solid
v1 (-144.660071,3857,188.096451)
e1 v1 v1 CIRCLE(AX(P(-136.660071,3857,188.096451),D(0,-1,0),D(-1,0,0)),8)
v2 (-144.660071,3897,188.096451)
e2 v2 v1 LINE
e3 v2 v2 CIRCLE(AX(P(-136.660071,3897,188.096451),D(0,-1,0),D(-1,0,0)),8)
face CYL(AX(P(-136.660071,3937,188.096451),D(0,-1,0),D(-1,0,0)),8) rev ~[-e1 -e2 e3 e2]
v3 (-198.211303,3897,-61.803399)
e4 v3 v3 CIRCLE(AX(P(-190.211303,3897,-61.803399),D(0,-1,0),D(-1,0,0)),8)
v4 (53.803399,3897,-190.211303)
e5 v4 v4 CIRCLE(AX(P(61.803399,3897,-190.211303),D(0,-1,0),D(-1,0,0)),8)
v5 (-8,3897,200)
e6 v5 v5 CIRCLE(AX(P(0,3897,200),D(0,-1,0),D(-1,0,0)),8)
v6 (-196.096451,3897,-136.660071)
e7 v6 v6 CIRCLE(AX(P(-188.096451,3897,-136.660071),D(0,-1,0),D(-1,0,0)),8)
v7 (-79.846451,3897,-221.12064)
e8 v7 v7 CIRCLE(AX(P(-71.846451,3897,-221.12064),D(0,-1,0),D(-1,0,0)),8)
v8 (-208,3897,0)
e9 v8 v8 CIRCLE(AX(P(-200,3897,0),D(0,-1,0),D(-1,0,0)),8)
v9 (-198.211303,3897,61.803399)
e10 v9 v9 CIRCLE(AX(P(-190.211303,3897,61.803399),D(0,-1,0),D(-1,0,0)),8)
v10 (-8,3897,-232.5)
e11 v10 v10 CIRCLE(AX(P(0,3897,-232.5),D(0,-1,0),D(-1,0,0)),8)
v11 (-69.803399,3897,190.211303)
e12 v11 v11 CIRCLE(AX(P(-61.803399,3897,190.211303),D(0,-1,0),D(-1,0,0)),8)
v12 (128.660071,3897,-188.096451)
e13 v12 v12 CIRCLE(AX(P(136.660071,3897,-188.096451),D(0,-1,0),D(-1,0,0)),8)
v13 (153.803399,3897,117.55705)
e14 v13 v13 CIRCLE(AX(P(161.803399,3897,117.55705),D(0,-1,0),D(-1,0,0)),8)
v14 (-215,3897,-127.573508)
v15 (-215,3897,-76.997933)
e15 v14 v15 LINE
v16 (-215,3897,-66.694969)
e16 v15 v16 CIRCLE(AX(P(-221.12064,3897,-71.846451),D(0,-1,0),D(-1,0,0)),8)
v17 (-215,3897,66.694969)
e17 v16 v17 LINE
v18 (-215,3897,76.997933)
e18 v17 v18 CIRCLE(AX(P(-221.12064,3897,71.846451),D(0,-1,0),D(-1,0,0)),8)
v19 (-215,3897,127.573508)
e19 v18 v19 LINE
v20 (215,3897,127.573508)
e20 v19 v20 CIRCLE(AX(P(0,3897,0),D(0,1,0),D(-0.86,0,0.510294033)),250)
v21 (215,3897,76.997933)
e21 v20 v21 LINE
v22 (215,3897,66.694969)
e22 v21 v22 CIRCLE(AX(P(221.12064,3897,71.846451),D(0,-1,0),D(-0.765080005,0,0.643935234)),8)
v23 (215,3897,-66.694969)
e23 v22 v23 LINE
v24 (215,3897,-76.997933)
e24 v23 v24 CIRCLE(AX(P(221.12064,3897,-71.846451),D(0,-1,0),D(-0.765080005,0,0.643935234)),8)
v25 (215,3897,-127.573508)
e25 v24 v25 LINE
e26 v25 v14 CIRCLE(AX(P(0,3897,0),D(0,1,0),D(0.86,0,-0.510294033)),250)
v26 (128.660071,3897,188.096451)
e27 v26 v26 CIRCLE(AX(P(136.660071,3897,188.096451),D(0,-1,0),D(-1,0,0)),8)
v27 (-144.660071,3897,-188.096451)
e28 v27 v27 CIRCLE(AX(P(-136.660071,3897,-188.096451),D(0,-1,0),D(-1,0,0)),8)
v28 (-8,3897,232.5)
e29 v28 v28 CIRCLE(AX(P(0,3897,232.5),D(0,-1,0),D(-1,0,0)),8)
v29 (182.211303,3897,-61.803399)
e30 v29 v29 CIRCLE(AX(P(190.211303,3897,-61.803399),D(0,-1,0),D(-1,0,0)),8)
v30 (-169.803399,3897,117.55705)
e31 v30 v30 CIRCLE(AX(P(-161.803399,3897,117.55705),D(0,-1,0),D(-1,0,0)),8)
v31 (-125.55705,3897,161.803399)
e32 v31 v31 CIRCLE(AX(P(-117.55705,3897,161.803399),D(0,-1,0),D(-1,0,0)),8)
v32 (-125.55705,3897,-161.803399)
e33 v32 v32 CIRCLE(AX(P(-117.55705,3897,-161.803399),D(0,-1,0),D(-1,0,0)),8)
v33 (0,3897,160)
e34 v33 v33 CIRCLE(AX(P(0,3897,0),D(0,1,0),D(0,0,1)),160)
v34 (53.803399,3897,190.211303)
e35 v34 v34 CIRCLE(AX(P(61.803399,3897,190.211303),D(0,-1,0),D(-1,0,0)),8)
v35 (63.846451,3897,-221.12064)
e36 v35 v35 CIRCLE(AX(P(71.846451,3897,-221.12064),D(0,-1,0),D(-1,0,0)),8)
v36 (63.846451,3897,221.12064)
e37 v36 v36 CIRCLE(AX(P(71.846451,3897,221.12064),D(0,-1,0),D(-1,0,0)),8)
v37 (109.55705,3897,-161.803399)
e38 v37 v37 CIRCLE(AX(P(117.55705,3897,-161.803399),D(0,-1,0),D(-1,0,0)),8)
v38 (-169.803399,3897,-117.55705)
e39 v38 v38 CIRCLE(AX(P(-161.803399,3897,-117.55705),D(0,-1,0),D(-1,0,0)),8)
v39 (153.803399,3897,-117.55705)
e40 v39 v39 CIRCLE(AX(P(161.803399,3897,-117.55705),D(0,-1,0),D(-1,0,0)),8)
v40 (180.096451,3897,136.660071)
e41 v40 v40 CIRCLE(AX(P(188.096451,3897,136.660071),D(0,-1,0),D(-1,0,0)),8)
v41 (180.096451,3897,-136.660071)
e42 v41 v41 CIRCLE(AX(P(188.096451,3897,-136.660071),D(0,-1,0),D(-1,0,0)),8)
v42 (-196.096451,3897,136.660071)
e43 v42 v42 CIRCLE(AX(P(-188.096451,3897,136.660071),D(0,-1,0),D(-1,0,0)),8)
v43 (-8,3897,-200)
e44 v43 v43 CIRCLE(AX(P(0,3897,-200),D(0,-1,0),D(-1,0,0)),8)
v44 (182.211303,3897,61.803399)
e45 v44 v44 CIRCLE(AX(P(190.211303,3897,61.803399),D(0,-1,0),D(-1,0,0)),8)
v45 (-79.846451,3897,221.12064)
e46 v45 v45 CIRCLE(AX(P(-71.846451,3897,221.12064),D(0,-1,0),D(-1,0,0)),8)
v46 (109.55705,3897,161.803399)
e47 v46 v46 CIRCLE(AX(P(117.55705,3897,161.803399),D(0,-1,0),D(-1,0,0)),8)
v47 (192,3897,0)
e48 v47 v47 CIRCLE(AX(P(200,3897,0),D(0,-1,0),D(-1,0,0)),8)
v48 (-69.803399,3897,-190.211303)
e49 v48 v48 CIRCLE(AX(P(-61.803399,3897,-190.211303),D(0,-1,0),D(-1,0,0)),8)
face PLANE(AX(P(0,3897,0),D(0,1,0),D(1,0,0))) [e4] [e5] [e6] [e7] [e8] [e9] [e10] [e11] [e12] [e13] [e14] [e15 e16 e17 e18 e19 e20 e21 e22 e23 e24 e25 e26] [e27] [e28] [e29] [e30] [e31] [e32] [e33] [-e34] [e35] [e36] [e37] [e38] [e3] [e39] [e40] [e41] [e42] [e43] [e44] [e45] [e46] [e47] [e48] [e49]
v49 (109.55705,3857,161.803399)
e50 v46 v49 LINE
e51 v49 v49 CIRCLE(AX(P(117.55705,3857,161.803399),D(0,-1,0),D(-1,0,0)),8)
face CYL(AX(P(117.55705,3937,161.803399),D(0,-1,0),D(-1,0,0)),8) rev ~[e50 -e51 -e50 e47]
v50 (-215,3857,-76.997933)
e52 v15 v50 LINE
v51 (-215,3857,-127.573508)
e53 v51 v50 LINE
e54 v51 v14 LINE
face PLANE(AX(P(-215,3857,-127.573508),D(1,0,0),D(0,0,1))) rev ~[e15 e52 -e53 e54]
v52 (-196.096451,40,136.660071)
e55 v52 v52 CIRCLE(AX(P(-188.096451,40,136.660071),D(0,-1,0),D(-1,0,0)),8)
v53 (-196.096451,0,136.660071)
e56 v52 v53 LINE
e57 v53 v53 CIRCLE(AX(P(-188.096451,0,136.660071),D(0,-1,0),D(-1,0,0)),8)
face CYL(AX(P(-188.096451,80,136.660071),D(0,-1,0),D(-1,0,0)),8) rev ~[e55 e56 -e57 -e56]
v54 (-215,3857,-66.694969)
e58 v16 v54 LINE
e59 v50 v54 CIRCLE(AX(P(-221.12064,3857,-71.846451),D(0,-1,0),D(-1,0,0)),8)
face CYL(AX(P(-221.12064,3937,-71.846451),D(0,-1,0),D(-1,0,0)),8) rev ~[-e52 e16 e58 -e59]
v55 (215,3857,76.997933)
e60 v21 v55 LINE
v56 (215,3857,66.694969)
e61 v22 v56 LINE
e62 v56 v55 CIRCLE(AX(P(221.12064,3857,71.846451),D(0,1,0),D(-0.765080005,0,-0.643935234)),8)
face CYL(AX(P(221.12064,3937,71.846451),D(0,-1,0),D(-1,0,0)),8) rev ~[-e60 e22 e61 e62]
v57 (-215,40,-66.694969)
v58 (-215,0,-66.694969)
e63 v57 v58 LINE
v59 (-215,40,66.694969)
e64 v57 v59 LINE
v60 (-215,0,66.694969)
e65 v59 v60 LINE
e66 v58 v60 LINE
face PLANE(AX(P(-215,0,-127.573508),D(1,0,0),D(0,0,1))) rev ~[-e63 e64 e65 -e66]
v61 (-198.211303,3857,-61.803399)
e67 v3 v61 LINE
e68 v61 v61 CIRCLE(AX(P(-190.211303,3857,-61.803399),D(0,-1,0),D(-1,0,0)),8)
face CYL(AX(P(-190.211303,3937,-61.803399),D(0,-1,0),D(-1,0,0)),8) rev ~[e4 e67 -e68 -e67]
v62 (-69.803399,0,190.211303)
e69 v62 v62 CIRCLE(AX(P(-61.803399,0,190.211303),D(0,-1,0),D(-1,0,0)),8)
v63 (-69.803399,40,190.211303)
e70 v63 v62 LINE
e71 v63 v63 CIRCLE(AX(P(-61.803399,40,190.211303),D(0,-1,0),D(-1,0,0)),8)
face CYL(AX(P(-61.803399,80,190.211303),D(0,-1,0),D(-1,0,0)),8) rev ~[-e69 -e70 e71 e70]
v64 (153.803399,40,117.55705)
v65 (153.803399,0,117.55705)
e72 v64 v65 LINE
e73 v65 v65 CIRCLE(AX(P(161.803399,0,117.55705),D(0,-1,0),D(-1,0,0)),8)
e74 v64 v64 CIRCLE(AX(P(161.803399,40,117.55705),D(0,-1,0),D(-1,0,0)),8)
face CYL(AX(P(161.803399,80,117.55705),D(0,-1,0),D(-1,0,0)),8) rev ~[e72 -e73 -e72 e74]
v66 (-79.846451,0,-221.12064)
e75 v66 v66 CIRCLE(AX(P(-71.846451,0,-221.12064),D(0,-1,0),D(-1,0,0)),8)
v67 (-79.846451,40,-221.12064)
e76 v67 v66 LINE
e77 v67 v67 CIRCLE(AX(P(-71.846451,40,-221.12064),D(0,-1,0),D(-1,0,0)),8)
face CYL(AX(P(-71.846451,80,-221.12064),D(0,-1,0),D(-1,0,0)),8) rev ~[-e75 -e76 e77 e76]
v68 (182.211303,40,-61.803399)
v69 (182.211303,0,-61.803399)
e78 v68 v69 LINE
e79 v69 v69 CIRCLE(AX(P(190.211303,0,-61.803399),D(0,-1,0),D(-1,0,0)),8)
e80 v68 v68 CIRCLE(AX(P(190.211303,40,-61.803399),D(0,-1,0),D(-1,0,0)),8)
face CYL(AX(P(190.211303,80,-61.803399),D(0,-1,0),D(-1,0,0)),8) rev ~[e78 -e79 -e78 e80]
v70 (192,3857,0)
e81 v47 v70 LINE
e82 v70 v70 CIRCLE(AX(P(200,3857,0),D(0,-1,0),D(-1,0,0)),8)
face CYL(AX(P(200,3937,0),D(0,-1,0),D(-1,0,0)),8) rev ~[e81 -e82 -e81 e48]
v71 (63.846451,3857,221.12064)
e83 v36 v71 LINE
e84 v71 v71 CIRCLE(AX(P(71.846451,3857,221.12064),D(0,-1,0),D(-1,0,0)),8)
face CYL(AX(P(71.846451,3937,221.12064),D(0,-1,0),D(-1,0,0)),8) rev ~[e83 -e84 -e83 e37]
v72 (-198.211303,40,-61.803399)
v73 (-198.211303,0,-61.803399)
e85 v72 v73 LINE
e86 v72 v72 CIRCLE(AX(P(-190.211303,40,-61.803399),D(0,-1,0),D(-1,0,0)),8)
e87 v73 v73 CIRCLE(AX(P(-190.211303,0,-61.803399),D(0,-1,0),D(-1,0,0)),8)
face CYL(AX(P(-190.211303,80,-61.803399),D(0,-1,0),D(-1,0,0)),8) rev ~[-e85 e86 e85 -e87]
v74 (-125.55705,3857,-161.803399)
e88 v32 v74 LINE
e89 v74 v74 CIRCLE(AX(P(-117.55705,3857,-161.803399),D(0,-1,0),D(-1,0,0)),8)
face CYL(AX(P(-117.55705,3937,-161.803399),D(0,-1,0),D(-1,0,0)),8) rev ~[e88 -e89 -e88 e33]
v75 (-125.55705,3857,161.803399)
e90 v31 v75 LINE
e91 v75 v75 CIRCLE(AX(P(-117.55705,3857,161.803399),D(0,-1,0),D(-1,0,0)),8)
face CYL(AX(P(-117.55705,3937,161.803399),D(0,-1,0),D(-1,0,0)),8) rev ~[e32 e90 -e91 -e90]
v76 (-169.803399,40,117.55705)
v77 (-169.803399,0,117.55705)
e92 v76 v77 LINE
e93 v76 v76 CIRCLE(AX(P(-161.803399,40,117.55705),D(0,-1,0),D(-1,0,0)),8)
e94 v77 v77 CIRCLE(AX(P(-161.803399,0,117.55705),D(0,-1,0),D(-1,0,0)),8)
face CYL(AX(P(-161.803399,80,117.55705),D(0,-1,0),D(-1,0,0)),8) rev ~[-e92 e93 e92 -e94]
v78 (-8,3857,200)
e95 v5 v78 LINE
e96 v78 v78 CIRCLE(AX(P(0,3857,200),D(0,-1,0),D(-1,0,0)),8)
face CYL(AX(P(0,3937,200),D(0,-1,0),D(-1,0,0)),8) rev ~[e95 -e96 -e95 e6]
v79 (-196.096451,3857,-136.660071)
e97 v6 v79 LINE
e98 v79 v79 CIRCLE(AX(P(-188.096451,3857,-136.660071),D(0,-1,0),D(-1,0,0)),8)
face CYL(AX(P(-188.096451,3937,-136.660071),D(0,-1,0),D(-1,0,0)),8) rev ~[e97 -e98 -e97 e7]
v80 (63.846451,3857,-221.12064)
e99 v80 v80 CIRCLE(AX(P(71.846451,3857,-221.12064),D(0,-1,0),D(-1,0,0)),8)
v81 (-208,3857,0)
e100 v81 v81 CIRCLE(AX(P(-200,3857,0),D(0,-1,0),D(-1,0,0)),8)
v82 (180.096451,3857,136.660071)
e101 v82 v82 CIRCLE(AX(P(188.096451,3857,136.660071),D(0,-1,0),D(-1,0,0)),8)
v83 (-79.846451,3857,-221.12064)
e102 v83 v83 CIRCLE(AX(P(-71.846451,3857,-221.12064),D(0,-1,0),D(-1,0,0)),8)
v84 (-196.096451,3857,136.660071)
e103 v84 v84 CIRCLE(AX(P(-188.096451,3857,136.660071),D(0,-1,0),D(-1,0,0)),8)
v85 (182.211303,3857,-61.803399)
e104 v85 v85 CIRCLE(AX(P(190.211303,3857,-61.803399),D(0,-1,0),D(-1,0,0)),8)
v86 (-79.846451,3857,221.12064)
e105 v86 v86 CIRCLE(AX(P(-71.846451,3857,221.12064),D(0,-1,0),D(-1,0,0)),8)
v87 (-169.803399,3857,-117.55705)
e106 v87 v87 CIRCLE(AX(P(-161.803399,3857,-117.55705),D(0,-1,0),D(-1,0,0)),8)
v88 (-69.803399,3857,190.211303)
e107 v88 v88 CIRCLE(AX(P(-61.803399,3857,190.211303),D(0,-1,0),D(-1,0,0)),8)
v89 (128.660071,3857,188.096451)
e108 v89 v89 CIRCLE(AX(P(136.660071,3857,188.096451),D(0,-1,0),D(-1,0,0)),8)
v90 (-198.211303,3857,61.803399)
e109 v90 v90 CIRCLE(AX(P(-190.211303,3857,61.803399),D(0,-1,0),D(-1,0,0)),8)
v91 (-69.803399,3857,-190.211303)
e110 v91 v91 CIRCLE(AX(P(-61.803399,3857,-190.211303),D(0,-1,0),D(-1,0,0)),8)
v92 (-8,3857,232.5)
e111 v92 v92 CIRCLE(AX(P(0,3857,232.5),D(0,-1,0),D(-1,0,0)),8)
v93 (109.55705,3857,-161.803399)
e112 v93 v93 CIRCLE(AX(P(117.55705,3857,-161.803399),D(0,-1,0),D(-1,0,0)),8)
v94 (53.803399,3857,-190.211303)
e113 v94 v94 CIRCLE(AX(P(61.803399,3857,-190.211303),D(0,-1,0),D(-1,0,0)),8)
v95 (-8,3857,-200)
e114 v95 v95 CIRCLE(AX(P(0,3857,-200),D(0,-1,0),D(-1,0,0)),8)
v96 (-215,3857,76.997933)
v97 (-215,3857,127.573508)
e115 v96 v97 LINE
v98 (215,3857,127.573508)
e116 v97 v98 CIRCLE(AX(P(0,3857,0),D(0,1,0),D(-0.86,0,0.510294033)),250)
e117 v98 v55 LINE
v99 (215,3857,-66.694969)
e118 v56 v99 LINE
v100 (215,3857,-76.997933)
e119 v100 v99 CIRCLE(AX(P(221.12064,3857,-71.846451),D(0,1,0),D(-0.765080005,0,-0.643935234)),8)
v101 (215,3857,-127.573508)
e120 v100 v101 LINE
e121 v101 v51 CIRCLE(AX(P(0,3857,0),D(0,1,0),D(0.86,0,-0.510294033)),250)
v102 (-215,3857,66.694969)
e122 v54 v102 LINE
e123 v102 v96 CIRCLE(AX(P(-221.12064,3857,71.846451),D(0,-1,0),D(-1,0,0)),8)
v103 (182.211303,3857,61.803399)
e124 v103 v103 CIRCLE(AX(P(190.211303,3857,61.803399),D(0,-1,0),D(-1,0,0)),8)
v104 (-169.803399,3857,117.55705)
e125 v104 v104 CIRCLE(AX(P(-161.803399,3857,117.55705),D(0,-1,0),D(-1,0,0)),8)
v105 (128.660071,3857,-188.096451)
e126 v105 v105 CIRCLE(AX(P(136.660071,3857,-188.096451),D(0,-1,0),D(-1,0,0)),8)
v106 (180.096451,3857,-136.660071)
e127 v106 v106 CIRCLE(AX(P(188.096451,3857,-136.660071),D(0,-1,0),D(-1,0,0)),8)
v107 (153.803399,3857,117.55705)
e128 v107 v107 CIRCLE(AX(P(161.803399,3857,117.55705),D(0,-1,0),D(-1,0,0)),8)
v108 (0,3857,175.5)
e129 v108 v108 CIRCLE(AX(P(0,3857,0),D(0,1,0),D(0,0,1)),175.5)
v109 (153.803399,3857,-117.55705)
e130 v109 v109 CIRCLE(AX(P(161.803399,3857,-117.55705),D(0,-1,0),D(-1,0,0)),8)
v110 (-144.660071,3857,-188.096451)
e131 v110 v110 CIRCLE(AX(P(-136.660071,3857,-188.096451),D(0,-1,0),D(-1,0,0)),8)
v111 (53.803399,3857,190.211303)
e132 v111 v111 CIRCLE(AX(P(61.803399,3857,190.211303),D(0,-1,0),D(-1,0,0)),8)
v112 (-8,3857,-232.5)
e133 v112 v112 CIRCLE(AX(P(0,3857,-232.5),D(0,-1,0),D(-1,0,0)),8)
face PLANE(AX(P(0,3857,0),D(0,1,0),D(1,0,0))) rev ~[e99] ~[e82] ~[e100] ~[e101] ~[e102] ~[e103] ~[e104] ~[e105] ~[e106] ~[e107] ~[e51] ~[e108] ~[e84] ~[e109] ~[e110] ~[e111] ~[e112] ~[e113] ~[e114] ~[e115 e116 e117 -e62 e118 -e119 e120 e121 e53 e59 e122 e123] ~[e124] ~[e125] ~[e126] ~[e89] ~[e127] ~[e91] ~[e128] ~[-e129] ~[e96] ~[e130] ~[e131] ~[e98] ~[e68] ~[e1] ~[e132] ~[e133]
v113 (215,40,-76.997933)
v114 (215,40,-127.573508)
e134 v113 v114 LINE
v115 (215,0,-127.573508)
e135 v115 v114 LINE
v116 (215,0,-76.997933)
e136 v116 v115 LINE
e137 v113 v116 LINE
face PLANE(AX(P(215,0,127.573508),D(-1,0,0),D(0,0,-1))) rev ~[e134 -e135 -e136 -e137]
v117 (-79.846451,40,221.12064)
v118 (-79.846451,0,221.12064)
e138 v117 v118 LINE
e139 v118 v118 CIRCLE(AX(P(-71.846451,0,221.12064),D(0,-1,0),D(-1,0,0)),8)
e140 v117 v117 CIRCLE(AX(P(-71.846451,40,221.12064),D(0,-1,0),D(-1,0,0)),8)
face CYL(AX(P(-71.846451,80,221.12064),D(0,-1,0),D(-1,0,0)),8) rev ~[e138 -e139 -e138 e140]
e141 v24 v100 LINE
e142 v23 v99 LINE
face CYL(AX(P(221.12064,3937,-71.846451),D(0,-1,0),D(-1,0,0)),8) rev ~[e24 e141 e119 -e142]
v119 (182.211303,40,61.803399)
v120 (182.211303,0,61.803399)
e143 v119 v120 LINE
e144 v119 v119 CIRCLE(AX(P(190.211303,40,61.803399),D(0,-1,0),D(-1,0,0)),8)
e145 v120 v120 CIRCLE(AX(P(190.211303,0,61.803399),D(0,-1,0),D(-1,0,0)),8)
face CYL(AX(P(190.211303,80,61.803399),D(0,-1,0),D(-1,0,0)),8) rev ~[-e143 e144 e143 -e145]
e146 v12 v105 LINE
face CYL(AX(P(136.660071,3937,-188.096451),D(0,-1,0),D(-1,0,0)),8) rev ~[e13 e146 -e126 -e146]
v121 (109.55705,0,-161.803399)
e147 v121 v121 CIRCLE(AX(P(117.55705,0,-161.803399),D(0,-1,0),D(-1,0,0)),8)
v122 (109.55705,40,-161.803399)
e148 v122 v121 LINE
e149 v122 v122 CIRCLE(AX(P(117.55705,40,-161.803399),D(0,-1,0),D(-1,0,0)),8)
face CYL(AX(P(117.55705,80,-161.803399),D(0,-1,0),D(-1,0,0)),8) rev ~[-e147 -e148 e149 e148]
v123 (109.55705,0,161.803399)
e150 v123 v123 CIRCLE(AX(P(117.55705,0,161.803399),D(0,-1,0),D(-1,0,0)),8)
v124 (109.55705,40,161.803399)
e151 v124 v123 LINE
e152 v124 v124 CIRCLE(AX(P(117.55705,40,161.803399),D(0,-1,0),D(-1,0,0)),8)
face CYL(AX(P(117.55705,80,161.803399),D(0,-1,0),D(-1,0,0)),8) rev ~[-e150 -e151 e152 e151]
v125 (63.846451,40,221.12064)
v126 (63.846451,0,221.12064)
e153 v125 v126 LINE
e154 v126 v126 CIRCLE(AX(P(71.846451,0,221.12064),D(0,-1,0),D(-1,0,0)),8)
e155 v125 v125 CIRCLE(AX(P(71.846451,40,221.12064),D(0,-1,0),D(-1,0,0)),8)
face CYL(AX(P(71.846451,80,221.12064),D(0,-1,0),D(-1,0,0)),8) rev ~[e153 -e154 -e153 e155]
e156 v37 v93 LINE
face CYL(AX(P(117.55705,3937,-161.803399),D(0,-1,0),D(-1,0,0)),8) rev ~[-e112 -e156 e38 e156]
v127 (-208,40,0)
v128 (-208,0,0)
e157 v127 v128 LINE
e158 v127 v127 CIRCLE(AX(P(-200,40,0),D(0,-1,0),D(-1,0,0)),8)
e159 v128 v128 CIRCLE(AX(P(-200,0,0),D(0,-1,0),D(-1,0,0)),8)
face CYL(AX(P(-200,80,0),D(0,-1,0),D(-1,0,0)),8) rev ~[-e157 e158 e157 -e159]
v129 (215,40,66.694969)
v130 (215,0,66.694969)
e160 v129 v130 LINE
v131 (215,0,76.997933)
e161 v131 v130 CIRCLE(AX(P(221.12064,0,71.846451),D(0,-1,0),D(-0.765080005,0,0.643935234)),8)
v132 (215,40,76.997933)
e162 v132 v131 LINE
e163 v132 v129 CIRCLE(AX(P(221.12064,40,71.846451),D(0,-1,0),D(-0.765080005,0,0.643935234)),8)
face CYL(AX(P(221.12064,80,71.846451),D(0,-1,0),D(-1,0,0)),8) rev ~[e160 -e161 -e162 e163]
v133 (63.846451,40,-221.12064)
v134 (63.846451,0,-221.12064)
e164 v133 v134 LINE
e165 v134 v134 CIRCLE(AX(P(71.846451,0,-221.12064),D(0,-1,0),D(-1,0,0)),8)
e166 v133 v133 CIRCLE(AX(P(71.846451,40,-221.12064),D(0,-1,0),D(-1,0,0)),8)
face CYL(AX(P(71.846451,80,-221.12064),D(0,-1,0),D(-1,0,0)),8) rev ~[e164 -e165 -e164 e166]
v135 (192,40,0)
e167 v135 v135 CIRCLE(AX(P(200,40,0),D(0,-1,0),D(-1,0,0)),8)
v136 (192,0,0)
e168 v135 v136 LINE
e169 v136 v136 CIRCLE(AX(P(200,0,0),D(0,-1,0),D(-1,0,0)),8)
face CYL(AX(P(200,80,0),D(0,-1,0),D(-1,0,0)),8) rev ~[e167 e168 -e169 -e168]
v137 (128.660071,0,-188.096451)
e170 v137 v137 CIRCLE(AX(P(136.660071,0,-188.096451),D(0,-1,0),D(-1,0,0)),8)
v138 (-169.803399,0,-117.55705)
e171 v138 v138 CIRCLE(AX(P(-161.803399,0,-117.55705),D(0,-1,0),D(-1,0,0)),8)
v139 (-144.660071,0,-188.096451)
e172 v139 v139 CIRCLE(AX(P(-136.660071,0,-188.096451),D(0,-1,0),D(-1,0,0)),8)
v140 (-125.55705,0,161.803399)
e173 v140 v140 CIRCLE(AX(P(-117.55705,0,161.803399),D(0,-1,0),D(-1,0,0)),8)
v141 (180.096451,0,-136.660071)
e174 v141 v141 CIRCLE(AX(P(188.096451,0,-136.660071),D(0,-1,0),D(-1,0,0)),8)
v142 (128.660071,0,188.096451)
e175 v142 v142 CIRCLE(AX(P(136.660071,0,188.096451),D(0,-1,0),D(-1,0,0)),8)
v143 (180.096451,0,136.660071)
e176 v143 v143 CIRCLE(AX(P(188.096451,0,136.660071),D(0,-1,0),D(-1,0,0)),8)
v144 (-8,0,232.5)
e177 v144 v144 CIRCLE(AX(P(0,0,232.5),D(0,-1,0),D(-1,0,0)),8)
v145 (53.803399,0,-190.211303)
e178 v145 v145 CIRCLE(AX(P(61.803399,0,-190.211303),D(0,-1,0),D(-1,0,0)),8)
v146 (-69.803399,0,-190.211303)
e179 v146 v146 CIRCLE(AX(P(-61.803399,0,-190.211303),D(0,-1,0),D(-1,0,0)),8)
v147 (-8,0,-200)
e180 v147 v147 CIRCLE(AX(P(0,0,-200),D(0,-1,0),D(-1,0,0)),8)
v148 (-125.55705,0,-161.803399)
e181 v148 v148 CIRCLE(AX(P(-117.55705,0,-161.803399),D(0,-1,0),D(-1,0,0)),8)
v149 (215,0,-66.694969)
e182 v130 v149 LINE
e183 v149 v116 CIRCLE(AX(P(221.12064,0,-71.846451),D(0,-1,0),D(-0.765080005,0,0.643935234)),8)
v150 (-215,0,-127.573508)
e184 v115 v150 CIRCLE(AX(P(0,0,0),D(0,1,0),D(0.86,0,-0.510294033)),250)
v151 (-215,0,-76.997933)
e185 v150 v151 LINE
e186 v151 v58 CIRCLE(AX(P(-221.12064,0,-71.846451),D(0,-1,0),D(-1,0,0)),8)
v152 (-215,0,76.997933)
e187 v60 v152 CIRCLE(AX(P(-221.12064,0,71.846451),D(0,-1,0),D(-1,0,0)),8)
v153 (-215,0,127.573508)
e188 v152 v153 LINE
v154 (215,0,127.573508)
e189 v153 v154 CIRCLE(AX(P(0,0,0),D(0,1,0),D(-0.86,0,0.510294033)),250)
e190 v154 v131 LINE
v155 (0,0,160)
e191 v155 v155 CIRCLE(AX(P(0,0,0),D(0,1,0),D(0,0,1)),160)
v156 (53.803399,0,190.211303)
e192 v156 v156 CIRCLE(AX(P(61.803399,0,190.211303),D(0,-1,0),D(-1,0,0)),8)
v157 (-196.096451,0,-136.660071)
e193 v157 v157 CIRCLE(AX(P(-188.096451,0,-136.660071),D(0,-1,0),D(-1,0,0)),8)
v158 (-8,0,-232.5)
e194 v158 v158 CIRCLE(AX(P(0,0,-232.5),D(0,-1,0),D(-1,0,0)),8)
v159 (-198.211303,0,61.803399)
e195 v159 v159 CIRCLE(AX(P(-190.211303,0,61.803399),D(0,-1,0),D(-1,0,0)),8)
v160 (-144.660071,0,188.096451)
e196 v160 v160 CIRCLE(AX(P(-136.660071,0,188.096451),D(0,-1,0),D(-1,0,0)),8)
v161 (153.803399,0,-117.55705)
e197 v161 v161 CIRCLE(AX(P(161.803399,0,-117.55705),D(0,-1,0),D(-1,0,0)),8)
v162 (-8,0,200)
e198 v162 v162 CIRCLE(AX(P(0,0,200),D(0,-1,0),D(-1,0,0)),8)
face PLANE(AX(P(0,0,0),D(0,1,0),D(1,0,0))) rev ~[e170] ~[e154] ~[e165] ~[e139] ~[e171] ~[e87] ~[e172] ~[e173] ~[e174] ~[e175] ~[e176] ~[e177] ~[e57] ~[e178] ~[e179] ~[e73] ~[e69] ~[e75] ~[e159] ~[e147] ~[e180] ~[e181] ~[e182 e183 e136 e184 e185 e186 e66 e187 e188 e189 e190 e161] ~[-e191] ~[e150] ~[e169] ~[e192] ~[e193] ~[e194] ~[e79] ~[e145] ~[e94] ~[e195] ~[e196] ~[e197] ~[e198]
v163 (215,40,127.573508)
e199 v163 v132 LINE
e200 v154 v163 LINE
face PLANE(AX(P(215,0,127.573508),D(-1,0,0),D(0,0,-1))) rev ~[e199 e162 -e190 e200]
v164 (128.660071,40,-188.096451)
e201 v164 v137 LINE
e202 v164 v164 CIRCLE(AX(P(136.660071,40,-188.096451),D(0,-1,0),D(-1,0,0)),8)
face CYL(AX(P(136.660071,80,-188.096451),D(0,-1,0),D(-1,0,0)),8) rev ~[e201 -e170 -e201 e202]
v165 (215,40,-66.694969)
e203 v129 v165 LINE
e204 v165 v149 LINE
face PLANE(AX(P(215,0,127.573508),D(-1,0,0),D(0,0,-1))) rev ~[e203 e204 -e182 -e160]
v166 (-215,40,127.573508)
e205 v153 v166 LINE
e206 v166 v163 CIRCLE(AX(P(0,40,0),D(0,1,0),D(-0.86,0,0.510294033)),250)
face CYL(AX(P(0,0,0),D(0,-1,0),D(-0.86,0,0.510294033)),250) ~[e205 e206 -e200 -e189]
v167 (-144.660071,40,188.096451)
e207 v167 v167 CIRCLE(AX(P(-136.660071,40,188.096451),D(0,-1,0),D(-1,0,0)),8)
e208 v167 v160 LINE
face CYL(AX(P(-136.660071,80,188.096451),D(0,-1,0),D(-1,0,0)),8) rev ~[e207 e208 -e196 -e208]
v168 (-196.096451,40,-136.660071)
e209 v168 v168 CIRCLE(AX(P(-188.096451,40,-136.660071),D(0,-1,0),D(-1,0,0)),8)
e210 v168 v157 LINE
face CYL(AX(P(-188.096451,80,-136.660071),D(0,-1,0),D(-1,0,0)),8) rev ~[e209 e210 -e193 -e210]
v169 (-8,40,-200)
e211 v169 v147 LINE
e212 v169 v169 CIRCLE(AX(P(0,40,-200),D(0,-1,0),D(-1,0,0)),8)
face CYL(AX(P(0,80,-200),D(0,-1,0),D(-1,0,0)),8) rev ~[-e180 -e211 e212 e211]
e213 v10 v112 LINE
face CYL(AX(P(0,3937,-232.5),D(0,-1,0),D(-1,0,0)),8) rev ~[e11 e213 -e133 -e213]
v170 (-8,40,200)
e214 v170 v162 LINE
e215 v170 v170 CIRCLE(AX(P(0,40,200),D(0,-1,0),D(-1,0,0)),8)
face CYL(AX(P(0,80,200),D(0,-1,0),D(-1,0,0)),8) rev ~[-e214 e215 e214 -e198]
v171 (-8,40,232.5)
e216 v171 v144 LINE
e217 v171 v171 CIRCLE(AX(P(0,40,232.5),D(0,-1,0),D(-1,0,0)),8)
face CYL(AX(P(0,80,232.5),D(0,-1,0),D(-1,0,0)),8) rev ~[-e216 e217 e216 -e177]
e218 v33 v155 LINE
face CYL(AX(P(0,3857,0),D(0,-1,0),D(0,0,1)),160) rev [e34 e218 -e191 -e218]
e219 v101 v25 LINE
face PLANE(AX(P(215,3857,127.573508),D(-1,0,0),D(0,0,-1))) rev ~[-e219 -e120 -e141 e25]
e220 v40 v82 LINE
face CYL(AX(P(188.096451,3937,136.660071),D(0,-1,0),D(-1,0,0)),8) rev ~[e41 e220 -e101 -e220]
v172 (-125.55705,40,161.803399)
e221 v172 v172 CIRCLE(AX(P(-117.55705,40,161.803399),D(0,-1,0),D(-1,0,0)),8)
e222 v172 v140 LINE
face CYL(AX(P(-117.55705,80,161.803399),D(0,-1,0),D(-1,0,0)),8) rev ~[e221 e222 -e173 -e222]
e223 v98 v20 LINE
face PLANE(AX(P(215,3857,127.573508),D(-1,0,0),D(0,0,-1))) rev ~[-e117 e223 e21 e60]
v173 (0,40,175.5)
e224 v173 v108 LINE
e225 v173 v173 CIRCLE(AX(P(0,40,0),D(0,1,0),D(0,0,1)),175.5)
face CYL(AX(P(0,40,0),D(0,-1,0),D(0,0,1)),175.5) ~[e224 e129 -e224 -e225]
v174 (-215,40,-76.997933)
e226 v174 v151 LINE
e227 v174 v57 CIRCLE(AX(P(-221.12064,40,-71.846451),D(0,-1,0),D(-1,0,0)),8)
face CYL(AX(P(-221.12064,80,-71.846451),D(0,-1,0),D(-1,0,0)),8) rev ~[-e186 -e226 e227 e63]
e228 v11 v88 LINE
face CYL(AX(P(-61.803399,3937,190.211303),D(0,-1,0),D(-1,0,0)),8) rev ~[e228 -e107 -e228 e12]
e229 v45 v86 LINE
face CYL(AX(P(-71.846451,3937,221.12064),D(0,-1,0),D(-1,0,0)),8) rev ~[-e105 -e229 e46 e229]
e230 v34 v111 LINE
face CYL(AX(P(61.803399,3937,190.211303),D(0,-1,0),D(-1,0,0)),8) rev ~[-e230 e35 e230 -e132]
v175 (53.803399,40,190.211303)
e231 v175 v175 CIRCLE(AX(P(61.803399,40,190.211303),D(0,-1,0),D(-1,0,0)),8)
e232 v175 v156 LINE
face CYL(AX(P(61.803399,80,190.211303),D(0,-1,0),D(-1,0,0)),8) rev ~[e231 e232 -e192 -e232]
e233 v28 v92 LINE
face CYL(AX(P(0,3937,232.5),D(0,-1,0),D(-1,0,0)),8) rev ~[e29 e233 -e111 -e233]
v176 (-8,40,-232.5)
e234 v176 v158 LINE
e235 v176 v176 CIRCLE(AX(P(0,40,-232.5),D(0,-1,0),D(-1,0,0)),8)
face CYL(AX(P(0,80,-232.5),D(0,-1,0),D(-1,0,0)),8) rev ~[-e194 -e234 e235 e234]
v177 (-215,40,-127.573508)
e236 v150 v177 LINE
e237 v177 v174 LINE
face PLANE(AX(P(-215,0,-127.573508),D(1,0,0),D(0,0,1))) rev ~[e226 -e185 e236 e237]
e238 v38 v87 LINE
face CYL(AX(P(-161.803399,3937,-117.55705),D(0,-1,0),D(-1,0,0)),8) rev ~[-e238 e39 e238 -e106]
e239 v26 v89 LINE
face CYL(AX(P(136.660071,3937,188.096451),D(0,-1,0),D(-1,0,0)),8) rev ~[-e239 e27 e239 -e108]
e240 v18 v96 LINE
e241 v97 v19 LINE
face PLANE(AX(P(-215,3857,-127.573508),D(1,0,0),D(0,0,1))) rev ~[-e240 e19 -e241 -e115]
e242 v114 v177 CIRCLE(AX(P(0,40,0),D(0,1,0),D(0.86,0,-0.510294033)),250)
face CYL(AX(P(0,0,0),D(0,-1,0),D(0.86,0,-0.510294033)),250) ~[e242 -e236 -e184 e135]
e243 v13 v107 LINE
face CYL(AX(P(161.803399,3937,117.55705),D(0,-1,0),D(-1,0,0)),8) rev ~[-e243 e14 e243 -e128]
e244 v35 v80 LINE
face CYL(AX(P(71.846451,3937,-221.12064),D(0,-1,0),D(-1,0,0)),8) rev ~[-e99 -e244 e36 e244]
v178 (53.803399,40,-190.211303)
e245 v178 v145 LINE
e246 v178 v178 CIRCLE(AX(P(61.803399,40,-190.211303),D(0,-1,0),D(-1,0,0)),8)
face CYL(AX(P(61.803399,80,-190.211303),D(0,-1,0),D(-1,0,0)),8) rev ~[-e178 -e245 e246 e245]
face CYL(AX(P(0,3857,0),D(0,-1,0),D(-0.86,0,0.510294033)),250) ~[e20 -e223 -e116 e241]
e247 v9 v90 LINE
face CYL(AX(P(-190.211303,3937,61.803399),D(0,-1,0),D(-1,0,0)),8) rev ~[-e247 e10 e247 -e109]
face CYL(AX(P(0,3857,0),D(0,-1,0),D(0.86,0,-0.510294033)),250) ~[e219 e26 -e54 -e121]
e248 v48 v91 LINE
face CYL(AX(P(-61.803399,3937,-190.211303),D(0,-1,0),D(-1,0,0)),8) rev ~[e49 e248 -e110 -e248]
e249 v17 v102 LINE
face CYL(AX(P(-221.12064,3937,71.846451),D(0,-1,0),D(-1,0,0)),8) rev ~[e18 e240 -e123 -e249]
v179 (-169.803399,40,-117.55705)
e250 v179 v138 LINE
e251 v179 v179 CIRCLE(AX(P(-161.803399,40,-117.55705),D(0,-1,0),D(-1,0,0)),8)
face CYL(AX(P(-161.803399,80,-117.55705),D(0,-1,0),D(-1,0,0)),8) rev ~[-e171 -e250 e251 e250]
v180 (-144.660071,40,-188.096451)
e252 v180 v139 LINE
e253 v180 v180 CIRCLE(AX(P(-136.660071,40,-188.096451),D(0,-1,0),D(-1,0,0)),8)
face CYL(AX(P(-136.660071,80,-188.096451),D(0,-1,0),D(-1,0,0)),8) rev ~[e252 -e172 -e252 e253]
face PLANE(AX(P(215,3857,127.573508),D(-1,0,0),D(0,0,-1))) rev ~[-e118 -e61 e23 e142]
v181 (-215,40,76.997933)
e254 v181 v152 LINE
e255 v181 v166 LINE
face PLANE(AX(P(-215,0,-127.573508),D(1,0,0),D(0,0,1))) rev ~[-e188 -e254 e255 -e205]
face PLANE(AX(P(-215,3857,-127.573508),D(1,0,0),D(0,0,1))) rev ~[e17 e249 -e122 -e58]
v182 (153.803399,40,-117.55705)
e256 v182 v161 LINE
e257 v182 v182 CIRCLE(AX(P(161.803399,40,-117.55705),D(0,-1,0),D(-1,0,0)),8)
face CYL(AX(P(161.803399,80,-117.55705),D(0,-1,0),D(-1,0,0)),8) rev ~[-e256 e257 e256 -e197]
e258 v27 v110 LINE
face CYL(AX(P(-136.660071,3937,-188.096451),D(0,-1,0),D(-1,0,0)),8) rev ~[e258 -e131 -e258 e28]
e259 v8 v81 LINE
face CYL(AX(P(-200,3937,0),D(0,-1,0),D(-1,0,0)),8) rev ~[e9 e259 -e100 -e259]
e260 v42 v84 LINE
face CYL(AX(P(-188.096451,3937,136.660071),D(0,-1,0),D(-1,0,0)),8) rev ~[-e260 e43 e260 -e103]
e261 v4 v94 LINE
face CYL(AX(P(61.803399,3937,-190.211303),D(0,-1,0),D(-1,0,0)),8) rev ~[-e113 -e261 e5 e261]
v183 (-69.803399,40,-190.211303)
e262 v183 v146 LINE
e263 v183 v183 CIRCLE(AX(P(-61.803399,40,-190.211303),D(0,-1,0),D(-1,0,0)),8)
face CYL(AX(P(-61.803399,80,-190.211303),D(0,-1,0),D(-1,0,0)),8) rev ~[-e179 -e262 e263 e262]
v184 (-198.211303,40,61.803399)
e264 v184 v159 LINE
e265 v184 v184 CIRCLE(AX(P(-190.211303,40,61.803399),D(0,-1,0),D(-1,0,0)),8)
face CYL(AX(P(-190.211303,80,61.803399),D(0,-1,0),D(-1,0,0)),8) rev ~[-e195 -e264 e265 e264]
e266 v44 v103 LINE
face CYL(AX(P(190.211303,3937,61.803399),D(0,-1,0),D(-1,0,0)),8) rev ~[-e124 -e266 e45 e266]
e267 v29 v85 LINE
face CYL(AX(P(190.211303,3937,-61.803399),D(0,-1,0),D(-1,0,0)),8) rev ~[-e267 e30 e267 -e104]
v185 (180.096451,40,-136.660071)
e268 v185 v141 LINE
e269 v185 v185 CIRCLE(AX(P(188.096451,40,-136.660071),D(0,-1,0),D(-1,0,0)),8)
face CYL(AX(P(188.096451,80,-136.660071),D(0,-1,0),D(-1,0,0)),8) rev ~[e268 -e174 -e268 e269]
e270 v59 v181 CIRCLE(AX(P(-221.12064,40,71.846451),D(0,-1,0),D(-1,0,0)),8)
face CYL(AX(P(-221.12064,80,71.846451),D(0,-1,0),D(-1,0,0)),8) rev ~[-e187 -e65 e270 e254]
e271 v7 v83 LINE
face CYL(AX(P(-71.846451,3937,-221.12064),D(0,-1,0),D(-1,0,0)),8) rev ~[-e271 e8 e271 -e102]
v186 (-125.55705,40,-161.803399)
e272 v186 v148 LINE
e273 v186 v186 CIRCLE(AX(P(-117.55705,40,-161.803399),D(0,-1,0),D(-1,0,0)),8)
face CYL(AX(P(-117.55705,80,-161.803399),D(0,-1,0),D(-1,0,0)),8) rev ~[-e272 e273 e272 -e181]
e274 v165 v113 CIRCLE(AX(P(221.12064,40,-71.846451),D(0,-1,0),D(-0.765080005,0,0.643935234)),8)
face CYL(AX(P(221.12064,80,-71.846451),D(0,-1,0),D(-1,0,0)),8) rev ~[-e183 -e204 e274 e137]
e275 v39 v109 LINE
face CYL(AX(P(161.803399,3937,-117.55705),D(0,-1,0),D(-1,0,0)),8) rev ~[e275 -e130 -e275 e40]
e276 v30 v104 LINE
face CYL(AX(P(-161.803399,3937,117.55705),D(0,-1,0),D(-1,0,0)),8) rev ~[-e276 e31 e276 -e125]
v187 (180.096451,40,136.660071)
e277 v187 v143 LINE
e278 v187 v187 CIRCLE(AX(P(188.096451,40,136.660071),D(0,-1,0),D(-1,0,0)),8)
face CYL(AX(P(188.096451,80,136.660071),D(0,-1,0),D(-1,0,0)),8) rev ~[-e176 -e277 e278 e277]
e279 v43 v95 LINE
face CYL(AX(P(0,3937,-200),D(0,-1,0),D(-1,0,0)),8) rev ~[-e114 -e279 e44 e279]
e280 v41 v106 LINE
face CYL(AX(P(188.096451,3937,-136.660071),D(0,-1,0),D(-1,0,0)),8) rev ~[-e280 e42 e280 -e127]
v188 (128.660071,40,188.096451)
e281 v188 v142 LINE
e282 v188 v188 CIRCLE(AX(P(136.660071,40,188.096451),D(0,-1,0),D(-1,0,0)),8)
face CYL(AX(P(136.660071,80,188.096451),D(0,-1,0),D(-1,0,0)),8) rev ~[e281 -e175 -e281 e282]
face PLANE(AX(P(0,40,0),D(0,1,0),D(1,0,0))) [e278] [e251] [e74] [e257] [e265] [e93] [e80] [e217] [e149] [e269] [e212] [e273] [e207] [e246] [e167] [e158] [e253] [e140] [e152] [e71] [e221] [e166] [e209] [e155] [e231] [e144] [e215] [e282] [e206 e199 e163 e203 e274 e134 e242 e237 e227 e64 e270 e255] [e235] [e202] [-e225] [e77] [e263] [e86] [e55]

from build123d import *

# Parameters (mm, degrees)
SKETCH1_R                      = 160
BOSS_EXTRUDE1_DEPTH            = 40
SKETCH2_R                      = 175.5
SKETCH2_R_2                    = 160
BOSS_EXTRUDE2_DEPTH            = 3817
F_16_0_16_DIAMETER_HOLE1_D     = 16
F_16_0_16_DIAMETER_HOLE1_DEPTH = 40
LPATTERN1_COUNT                = 2
LPATTERN1_PITCH                = 3857


with BuildPart() as part:
    # Sketch1 → Boss-Extrude1 (new body)
    with BuildSketch(Plane(origin=(0, 0, 0), x_dir=(1, 0, 0), z_dir=(0, 1, 0))):
        with BuildLine():
            ThreePointArc((-215, -127.573508222), (0, -250), (215, -127.573508222))
            Line((215, -127.573508222), (215, 127.573508222))
            ThreePointArc((215, 127.573508222), (0, 250), (-215, 127.573508222))
            Line((-215, 127.573508222), (-215, -127.573508222))
        make_face()
        with Locations(Location((0, 0, 0), (0, 0, 270))):
            Circle(SKETCH1_R, mode=Mode.SUBTRACT)
    boss_extrude1 = extrude(amount=BOSS_EXTRUDE1_DEPTH)

    # Sketch2 → Boss-Extrude2 (add)
    with BuildSketch(Plane(origin=(0, 40, 0), x_dir=(1, 0, 0), z_dir=(0, 1, 0))):
        with Locations(Location((0, 0, 0), (0, 0, 270))):
            Circle(SKETCH2_R)
        with Locations(Location((0, 0, 0), (0, 0, 270))):
            Circle(SKETCH2_R_2, mode=Mode.SUBTRACT)
    extrude(amount=BOSS_EXTRUDE2_DEPTH)

    # Ø16.0 (16) Diameter Hole1
    with Locations(Plane(origin=(0, 40, 0), x_dir=(1, 0, 0), z_dir=(0, 1, 0))):
        with Locations((200, 0), (190.211303259, -61.803398875), (161.803398875, -117.557050458), (117.557050458, -161.803398875), (61.803398875, -190.211303259), (0, -200), (-61.803398875, -190.211303259), (-117.557050458, -161.803398875), (-161.803398875, -117.557050458), (-190.211303259, -61.803398875), (-200, 0), (-190.211303259, 61.803398875), (-161.803398875, 117.557050458), (-117.557050458, 161.803398875), (-61.803398875, 190.211303259), (0, 200), (61.803398875, 190.211303259), (117.557050458, 161.803398875), (161.803398875, 117.557050458), (190.211303259, 61.803398875), (232.5, 0), (221.120640039, -71.846451192), (188.096451192, -136.660071158), (136.660071158, -188.096451192), (71.846451192, -221.120640039), (0, -232.5), (-71.846451192, -221.120640039), (-136.660071158, -188.096451192), (-188.096451192, -136.660071158), (-221.120640039, -71.846451192), (-232.5, 0), (-221.120640039, 71.846451192), (-188.096451192, 136.660071158), (-136.660071158, 188.096451192), (-71.846451192, 221.120640039), (0, 232.5), (71.846451192, 221.120640039), (136.660071158, 188.096451192), (188.096451192, 136.660071158), (221.120640039, 71.846451192)):
            f_16_0_16_diameter_hole1 = Hole(F_16_0_16_DIAMETER_HOLE1_D / 2, depth=F_16_0_16_DIAMETER_HOLE1_DEPTH)

    # LPattern1: Boss-Extrude1, Ø16.0 (16) Diameter Hole1 ×2
    with Locations(*[(0, i * LPATTERN1_PITCH, 0) for i in range(1, LPATTERN1_COUNT)]):
        add(boss_extrude1)
        add(f_16_0_16_diameter_hole1, mode=Mode.SUBTRACT)


solid = part.part
